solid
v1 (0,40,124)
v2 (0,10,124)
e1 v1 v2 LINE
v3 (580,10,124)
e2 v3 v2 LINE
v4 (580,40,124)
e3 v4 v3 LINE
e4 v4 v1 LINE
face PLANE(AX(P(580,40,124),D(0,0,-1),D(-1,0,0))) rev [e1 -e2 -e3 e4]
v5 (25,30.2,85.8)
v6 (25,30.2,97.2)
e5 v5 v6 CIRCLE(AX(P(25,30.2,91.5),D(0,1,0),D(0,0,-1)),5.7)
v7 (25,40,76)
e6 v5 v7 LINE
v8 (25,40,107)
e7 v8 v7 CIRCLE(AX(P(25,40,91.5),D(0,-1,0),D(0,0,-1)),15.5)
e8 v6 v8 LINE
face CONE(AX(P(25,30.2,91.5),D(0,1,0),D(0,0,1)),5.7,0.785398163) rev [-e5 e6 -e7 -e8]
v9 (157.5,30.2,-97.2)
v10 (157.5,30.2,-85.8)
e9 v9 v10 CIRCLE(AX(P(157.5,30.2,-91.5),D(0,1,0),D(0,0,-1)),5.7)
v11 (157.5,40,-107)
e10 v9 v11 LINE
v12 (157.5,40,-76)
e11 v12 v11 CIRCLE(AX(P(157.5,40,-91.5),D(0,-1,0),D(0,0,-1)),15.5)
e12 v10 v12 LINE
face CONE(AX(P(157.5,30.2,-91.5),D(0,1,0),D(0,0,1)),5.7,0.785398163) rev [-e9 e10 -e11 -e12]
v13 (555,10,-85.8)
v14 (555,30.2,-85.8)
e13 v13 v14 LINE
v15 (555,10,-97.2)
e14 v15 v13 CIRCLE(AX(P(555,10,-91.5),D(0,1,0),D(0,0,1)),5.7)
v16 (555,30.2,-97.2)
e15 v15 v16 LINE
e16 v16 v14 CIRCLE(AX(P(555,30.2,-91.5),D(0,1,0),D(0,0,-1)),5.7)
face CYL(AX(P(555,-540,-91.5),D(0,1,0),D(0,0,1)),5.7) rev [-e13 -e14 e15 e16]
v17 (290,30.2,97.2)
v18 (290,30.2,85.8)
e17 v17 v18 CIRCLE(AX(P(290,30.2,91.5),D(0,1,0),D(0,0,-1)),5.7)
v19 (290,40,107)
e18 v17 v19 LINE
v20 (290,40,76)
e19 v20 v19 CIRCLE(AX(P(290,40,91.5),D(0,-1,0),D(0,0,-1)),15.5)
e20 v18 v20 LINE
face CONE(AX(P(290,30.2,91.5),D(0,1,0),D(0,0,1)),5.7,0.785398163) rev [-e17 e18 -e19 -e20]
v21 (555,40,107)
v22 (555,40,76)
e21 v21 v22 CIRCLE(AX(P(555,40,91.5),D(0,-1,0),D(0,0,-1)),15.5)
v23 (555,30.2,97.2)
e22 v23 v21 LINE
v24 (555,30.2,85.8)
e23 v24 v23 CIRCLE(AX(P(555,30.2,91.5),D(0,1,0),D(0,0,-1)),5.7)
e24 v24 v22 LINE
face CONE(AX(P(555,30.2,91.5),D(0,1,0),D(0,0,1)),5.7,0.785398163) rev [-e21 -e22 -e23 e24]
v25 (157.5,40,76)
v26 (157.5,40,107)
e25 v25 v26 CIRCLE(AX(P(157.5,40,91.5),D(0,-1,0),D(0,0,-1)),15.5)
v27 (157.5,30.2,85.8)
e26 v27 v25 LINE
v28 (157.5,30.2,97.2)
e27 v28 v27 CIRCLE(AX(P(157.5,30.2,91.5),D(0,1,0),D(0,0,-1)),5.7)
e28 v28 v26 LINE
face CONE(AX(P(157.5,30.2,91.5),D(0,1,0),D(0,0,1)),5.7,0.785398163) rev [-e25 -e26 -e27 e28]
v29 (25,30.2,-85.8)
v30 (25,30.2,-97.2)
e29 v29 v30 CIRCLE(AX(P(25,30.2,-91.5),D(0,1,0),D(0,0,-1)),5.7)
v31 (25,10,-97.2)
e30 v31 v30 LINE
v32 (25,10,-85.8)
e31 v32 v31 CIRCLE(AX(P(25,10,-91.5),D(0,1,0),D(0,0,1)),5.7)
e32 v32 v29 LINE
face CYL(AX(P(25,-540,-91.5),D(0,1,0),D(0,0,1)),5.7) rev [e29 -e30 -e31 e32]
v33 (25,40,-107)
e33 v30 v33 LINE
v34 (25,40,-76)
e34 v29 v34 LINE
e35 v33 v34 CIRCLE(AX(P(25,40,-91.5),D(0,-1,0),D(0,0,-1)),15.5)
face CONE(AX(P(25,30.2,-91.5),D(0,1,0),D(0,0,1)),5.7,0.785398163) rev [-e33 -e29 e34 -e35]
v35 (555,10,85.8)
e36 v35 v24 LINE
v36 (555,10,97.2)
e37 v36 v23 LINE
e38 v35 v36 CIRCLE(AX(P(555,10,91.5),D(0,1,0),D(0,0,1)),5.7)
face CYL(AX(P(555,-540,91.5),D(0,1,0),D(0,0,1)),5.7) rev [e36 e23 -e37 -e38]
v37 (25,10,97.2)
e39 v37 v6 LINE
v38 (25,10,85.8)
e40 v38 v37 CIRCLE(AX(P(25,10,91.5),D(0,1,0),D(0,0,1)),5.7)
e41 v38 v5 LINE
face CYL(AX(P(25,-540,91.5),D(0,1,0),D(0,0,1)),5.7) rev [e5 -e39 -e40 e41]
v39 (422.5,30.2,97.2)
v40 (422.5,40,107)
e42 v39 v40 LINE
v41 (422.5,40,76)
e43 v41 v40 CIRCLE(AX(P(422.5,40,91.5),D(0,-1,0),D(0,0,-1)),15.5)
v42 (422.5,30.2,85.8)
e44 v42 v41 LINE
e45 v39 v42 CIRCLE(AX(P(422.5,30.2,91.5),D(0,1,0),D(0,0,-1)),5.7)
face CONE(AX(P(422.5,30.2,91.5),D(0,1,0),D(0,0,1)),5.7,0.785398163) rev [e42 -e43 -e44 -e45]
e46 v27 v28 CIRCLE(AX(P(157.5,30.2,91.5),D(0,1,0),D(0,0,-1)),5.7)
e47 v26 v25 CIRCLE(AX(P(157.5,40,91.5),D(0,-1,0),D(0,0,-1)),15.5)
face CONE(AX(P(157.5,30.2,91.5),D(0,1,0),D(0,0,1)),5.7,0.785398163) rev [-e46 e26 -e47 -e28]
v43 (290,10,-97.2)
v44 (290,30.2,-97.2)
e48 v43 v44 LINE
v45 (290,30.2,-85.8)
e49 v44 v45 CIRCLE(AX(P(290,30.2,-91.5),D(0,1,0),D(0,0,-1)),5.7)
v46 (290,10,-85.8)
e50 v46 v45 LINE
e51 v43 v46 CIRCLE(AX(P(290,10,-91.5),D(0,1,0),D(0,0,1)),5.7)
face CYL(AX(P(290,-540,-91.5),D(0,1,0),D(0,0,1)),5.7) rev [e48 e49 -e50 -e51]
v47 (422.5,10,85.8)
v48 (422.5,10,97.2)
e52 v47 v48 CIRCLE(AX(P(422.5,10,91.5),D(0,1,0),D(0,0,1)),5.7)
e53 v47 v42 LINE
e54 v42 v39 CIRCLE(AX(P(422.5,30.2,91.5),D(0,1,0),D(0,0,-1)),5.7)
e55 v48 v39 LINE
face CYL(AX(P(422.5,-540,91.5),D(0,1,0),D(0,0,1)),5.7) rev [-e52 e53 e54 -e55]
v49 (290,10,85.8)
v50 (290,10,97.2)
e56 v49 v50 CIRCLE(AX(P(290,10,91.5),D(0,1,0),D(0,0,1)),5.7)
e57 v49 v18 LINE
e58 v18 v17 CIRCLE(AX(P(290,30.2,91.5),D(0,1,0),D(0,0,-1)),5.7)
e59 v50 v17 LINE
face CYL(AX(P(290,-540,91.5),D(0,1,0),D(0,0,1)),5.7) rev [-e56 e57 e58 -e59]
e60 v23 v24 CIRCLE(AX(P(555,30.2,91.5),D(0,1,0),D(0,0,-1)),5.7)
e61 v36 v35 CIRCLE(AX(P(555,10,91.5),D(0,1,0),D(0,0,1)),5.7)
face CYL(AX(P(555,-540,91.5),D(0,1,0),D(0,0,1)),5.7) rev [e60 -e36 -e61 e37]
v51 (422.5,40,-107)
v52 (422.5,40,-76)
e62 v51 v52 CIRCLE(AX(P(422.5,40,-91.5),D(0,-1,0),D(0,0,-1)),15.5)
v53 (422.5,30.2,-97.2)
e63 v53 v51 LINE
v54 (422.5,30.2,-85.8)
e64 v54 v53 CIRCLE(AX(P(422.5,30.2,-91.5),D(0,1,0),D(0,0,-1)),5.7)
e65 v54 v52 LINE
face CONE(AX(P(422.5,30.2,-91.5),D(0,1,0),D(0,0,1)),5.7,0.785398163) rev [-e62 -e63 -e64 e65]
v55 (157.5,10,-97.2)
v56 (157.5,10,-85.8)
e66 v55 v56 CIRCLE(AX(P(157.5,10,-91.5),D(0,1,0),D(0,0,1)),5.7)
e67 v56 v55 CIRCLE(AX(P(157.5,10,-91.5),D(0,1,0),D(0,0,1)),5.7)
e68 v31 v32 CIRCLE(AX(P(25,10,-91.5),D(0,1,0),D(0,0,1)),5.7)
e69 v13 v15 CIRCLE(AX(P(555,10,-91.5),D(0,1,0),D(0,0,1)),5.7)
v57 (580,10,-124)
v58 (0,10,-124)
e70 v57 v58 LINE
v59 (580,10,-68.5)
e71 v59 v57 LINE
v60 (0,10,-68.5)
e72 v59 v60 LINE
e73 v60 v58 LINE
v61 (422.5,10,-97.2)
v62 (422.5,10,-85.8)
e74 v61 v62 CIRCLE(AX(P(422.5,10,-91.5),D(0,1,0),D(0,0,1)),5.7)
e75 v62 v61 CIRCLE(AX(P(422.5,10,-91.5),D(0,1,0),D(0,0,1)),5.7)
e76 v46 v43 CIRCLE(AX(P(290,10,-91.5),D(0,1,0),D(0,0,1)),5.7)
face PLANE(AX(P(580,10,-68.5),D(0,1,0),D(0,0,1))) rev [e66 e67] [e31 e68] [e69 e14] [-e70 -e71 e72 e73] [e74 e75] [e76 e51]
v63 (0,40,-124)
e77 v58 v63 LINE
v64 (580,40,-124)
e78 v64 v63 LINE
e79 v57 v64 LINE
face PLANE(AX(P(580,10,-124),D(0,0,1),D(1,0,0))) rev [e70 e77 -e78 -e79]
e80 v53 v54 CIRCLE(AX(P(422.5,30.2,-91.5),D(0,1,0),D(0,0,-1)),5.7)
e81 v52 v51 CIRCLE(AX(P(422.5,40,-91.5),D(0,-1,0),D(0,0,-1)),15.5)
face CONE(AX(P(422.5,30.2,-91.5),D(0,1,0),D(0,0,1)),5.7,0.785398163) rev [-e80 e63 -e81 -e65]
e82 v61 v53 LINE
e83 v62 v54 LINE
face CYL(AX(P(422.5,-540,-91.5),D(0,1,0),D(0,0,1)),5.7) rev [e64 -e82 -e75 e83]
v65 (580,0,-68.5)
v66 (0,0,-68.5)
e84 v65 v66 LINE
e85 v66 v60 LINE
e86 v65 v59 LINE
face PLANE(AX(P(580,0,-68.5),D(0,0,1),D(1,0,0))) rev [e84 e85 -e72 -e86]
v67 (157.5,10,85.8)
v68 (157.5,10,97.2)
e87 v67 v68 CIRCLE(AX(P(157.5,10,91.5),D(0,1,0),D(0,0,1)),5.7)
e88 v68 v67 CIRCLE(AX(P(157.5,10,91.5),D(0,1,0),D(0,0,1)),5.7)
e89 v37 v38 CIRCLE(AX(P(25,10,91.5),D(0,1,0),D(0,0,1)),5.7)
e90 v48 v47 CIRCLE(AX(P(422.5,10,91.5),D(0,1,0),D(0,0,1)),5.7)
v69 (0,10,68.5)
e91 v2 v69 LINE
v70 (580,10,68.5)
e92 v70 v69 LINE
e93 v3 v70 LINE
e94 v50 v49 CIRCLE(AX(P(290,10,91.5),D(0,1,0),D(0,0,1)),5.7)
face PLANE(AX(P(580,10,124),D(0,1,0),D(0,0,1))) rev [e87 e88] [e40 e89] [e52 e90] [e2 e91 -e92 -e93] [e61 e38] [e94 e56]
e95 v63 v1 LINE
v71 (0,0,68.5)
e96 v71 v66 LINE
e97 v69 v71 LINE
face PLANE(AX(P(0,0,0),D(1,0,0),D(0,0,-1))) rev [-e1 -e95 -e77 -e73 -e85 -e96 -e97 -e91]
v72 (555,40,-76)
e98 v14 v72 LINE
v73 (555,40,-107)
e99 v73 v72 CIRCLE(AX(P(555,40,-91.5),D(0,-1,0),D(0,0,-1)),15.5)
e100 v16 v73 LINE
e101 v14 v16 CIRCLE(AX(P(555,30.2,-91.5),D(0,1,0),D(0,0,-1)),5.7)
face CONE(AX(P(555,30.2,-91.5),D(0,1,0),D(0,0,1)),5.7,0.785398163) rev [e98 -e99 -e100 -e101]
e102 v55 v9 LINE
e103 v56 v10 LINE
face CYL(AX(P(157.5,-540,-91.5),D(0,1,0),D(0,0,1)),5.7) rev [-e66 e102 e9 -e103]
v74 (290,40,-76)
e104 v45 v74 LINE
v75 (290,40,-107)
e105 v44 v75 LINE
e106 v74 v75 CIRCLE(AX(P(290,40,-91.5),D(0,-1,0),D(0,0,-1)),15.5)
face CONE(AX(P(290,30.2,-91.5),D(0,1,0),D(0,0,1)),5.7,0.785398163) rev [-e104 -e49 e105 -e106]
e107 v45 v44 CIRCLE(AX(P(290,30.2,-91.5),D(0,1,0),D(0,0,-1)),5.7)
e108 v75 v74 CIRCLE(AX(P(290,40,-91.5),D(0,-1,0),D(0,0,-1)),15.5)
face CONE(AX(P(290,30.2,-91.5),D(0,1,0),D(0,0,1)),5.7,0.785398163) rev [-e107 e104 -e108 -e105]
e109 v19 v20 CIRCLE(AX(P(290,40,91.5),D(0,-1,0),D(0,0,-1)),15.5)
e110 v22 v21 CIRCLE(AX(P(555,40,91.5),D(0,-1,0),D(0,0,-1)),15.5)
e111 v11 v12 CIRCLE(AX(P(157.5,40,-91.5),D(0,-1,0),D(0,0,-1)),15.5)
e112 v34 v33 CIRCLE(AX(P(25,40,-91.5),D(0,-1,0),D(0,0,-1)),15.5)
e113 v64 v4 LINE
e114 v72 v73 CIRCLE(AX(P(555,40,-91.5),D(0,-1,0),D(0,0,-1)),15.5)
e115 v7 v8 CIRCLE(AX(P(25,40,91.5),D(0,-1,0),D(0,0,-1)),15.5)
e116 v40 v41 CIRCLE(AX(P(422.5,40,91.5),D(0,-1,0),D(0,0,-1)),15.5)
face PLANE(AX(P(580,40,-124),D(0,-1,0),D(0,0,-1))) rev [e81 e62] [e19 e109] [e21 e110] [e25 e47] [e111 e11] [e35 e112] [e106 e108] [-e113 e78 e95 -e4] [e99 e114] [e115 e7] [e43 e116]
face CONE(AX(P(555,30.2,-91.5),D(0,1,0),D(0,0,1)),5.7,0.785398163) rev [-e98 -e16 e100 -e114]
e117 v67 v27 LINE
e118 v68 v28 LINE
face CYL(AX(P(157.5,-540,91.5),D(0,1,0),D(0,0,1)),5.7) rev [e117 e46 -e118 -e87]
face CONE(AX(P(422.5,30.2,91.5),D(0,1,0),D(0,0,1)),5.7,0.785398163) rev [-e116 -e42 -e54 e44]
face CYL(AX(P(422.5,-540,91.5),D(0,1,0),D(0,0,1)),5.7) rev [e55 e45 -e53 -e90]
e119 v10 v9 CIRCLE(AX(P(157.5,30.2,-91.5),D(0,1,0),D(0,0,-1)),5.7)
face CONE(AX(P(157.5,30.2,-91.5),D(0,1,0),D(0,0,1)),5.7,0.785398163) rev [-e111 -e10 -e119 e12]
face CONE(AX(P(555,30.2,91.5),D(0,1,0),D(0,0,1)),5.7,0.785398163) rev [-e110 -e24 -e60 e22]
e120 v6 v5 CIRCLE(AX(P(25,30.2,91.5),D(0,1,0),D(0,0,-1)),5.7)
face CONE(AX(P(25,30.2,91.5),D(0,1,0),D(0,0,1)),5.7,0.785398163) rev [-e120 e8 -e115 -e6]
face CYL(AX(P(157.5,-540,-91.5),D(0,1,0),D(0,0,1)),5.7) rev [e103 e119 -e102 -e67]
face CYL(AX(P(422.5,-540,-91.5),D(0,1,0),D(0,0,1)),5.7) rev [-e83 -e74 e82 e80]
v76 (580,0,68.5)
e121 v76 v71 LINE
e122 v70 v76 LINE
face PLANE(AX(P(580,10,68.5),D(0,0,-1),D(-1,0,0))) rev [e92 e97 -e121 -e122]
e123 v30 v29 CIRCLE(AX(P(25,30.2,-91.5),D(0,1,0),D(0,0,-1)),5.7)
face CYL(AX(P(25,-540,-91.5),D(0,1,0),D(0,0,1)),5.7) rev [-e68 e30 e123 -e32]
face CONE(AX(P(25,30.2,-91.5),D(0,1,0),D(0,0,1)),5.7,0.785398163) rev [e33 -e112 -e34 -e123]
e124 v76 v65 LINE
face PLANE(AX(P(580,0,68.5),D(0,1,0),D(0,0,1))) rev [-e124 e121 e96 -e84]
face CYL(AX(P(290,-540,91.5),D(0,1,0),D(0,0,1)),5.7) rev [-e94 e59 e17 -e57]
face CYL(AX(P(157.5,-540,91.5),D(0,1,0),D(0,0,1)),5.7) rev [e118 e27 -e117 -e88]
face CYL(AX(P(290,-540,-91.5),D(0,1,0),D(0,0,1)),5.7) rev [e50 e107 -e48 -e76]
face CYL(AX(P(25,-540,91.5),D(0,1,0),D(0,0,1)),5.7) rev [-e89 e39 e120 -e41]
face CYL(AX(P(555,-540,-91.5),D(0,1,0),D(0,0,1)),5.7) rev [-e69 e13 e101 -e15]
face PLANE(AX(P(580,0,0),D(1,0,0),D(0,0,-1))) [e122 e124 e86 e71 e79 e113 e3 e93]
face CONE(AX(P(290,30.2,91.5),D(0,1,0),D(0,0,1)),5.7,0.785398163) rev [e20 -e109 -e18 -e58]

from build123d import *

# Parameters (mm, degrees)
BASE_PLATE_DEPTH           = 580
MOUNTING_HOLES_SKETCH_R    = 5.7
MOUNTING_HOLES_8X_11_DEPTH = 580
HOLE_CHAMFERS_6MM_SIZE     = 9.8


with BuildPart() as part:
    # Plate Profile Sketch → Base Plate (new body)
    with BuildSketch(Plane(origin=(0, 0, 0), x_dir=(0, 0, -1), z_dir=(1, 0, 0))):
        Polygon((-68.5, 0), (68.5, 0), (68.5, 10), (124, 10), (124, 40), (-124, 40), (-124, 10), (-68.5, 10), align=None)
    extrude(amount=BASE_PLATE_DEPTH)

    # Mounting Holes Sketch → Mounting Holes 8xØ11 (cut)
    with BuildSketch(Plane(origin=(0, 40, 0), x_dir=(1, 0, 0), z_dir=(0, 1, 0))):
        with Locations(Location((25, -91.5, 0), (0, 0, 270))):
            Circle(MOUNTING_HOLES_SKETCH_R)
        with Locations(Location((157.5, -91.5, 0), (0, 0, 270))):
            Circle(MOUNTING_HOLES_SKETCH_R)
        with Locations(Location((422.5, -91.5, 0), (0, 0, 270))):
            Circle(MOUNTING_HOLES_SKETCH_R)
        with Locations(Location((555, -91.5, 0), (0, 0, 270))):
            Circle(MOUNTING_HOLES_SKETCH_R)
        with Locations(Location((290, -91.5, 0), (0, 0, 270))):
            Circle(MOUNTING_HOLES_SKETCH_R)
        with Locations(Location((555, 91.5, 0), (0, 0, 270))):
            Circle(MOUNTING_HOLES_SKETCH_R)
        with Locations(Location((422.5, 91.5, 0), (0, 0, 270))):
            Circle(MOUNTING_HOLES_SKETCH_R)
        with Locations(Location((290, 91.5, 0), (0, 0, 270))):
            Circle(MOUNTING_HOLES_SKETCH_R)
        with Locations(Location((157.5, 91.5, 0), (0, 0, 270))):
            Circle(MOUNTING_HOLES_SKETCH_R)
        with Locations(Location((25, 91.5, 0), (0, 0, 270))):
            Circle(MOUNTING_HOLES_SKETCH_R)
    extrude(amount=-MOUNTING_HOLES_8X_11_DEPTH, mode=Mode.SUBTRACT)

    # Hole Chamfers 6mm
    hole_chamfers_6mm_edges = [part.edges().sort_by_distance(p)[0] for p in [
        (25, 40, -97.2),
        (157.5, 40, -97.2),
        (290, 40, -97.2),
        (422.5, 40, -97.2),
        (555, 40, -97.2),
        (157.5, 40, 85.8),
        (422.5, 40, 85.8),
        (555, 40, 85.8),
        (290, 40, 85.8),
        (25, 40, 85.8),
    ]]
    chamfer(hole_chamfers_6mm_edges, length=HOLE_CHAMFERS_6MM_SIZE)


solid = part.part
